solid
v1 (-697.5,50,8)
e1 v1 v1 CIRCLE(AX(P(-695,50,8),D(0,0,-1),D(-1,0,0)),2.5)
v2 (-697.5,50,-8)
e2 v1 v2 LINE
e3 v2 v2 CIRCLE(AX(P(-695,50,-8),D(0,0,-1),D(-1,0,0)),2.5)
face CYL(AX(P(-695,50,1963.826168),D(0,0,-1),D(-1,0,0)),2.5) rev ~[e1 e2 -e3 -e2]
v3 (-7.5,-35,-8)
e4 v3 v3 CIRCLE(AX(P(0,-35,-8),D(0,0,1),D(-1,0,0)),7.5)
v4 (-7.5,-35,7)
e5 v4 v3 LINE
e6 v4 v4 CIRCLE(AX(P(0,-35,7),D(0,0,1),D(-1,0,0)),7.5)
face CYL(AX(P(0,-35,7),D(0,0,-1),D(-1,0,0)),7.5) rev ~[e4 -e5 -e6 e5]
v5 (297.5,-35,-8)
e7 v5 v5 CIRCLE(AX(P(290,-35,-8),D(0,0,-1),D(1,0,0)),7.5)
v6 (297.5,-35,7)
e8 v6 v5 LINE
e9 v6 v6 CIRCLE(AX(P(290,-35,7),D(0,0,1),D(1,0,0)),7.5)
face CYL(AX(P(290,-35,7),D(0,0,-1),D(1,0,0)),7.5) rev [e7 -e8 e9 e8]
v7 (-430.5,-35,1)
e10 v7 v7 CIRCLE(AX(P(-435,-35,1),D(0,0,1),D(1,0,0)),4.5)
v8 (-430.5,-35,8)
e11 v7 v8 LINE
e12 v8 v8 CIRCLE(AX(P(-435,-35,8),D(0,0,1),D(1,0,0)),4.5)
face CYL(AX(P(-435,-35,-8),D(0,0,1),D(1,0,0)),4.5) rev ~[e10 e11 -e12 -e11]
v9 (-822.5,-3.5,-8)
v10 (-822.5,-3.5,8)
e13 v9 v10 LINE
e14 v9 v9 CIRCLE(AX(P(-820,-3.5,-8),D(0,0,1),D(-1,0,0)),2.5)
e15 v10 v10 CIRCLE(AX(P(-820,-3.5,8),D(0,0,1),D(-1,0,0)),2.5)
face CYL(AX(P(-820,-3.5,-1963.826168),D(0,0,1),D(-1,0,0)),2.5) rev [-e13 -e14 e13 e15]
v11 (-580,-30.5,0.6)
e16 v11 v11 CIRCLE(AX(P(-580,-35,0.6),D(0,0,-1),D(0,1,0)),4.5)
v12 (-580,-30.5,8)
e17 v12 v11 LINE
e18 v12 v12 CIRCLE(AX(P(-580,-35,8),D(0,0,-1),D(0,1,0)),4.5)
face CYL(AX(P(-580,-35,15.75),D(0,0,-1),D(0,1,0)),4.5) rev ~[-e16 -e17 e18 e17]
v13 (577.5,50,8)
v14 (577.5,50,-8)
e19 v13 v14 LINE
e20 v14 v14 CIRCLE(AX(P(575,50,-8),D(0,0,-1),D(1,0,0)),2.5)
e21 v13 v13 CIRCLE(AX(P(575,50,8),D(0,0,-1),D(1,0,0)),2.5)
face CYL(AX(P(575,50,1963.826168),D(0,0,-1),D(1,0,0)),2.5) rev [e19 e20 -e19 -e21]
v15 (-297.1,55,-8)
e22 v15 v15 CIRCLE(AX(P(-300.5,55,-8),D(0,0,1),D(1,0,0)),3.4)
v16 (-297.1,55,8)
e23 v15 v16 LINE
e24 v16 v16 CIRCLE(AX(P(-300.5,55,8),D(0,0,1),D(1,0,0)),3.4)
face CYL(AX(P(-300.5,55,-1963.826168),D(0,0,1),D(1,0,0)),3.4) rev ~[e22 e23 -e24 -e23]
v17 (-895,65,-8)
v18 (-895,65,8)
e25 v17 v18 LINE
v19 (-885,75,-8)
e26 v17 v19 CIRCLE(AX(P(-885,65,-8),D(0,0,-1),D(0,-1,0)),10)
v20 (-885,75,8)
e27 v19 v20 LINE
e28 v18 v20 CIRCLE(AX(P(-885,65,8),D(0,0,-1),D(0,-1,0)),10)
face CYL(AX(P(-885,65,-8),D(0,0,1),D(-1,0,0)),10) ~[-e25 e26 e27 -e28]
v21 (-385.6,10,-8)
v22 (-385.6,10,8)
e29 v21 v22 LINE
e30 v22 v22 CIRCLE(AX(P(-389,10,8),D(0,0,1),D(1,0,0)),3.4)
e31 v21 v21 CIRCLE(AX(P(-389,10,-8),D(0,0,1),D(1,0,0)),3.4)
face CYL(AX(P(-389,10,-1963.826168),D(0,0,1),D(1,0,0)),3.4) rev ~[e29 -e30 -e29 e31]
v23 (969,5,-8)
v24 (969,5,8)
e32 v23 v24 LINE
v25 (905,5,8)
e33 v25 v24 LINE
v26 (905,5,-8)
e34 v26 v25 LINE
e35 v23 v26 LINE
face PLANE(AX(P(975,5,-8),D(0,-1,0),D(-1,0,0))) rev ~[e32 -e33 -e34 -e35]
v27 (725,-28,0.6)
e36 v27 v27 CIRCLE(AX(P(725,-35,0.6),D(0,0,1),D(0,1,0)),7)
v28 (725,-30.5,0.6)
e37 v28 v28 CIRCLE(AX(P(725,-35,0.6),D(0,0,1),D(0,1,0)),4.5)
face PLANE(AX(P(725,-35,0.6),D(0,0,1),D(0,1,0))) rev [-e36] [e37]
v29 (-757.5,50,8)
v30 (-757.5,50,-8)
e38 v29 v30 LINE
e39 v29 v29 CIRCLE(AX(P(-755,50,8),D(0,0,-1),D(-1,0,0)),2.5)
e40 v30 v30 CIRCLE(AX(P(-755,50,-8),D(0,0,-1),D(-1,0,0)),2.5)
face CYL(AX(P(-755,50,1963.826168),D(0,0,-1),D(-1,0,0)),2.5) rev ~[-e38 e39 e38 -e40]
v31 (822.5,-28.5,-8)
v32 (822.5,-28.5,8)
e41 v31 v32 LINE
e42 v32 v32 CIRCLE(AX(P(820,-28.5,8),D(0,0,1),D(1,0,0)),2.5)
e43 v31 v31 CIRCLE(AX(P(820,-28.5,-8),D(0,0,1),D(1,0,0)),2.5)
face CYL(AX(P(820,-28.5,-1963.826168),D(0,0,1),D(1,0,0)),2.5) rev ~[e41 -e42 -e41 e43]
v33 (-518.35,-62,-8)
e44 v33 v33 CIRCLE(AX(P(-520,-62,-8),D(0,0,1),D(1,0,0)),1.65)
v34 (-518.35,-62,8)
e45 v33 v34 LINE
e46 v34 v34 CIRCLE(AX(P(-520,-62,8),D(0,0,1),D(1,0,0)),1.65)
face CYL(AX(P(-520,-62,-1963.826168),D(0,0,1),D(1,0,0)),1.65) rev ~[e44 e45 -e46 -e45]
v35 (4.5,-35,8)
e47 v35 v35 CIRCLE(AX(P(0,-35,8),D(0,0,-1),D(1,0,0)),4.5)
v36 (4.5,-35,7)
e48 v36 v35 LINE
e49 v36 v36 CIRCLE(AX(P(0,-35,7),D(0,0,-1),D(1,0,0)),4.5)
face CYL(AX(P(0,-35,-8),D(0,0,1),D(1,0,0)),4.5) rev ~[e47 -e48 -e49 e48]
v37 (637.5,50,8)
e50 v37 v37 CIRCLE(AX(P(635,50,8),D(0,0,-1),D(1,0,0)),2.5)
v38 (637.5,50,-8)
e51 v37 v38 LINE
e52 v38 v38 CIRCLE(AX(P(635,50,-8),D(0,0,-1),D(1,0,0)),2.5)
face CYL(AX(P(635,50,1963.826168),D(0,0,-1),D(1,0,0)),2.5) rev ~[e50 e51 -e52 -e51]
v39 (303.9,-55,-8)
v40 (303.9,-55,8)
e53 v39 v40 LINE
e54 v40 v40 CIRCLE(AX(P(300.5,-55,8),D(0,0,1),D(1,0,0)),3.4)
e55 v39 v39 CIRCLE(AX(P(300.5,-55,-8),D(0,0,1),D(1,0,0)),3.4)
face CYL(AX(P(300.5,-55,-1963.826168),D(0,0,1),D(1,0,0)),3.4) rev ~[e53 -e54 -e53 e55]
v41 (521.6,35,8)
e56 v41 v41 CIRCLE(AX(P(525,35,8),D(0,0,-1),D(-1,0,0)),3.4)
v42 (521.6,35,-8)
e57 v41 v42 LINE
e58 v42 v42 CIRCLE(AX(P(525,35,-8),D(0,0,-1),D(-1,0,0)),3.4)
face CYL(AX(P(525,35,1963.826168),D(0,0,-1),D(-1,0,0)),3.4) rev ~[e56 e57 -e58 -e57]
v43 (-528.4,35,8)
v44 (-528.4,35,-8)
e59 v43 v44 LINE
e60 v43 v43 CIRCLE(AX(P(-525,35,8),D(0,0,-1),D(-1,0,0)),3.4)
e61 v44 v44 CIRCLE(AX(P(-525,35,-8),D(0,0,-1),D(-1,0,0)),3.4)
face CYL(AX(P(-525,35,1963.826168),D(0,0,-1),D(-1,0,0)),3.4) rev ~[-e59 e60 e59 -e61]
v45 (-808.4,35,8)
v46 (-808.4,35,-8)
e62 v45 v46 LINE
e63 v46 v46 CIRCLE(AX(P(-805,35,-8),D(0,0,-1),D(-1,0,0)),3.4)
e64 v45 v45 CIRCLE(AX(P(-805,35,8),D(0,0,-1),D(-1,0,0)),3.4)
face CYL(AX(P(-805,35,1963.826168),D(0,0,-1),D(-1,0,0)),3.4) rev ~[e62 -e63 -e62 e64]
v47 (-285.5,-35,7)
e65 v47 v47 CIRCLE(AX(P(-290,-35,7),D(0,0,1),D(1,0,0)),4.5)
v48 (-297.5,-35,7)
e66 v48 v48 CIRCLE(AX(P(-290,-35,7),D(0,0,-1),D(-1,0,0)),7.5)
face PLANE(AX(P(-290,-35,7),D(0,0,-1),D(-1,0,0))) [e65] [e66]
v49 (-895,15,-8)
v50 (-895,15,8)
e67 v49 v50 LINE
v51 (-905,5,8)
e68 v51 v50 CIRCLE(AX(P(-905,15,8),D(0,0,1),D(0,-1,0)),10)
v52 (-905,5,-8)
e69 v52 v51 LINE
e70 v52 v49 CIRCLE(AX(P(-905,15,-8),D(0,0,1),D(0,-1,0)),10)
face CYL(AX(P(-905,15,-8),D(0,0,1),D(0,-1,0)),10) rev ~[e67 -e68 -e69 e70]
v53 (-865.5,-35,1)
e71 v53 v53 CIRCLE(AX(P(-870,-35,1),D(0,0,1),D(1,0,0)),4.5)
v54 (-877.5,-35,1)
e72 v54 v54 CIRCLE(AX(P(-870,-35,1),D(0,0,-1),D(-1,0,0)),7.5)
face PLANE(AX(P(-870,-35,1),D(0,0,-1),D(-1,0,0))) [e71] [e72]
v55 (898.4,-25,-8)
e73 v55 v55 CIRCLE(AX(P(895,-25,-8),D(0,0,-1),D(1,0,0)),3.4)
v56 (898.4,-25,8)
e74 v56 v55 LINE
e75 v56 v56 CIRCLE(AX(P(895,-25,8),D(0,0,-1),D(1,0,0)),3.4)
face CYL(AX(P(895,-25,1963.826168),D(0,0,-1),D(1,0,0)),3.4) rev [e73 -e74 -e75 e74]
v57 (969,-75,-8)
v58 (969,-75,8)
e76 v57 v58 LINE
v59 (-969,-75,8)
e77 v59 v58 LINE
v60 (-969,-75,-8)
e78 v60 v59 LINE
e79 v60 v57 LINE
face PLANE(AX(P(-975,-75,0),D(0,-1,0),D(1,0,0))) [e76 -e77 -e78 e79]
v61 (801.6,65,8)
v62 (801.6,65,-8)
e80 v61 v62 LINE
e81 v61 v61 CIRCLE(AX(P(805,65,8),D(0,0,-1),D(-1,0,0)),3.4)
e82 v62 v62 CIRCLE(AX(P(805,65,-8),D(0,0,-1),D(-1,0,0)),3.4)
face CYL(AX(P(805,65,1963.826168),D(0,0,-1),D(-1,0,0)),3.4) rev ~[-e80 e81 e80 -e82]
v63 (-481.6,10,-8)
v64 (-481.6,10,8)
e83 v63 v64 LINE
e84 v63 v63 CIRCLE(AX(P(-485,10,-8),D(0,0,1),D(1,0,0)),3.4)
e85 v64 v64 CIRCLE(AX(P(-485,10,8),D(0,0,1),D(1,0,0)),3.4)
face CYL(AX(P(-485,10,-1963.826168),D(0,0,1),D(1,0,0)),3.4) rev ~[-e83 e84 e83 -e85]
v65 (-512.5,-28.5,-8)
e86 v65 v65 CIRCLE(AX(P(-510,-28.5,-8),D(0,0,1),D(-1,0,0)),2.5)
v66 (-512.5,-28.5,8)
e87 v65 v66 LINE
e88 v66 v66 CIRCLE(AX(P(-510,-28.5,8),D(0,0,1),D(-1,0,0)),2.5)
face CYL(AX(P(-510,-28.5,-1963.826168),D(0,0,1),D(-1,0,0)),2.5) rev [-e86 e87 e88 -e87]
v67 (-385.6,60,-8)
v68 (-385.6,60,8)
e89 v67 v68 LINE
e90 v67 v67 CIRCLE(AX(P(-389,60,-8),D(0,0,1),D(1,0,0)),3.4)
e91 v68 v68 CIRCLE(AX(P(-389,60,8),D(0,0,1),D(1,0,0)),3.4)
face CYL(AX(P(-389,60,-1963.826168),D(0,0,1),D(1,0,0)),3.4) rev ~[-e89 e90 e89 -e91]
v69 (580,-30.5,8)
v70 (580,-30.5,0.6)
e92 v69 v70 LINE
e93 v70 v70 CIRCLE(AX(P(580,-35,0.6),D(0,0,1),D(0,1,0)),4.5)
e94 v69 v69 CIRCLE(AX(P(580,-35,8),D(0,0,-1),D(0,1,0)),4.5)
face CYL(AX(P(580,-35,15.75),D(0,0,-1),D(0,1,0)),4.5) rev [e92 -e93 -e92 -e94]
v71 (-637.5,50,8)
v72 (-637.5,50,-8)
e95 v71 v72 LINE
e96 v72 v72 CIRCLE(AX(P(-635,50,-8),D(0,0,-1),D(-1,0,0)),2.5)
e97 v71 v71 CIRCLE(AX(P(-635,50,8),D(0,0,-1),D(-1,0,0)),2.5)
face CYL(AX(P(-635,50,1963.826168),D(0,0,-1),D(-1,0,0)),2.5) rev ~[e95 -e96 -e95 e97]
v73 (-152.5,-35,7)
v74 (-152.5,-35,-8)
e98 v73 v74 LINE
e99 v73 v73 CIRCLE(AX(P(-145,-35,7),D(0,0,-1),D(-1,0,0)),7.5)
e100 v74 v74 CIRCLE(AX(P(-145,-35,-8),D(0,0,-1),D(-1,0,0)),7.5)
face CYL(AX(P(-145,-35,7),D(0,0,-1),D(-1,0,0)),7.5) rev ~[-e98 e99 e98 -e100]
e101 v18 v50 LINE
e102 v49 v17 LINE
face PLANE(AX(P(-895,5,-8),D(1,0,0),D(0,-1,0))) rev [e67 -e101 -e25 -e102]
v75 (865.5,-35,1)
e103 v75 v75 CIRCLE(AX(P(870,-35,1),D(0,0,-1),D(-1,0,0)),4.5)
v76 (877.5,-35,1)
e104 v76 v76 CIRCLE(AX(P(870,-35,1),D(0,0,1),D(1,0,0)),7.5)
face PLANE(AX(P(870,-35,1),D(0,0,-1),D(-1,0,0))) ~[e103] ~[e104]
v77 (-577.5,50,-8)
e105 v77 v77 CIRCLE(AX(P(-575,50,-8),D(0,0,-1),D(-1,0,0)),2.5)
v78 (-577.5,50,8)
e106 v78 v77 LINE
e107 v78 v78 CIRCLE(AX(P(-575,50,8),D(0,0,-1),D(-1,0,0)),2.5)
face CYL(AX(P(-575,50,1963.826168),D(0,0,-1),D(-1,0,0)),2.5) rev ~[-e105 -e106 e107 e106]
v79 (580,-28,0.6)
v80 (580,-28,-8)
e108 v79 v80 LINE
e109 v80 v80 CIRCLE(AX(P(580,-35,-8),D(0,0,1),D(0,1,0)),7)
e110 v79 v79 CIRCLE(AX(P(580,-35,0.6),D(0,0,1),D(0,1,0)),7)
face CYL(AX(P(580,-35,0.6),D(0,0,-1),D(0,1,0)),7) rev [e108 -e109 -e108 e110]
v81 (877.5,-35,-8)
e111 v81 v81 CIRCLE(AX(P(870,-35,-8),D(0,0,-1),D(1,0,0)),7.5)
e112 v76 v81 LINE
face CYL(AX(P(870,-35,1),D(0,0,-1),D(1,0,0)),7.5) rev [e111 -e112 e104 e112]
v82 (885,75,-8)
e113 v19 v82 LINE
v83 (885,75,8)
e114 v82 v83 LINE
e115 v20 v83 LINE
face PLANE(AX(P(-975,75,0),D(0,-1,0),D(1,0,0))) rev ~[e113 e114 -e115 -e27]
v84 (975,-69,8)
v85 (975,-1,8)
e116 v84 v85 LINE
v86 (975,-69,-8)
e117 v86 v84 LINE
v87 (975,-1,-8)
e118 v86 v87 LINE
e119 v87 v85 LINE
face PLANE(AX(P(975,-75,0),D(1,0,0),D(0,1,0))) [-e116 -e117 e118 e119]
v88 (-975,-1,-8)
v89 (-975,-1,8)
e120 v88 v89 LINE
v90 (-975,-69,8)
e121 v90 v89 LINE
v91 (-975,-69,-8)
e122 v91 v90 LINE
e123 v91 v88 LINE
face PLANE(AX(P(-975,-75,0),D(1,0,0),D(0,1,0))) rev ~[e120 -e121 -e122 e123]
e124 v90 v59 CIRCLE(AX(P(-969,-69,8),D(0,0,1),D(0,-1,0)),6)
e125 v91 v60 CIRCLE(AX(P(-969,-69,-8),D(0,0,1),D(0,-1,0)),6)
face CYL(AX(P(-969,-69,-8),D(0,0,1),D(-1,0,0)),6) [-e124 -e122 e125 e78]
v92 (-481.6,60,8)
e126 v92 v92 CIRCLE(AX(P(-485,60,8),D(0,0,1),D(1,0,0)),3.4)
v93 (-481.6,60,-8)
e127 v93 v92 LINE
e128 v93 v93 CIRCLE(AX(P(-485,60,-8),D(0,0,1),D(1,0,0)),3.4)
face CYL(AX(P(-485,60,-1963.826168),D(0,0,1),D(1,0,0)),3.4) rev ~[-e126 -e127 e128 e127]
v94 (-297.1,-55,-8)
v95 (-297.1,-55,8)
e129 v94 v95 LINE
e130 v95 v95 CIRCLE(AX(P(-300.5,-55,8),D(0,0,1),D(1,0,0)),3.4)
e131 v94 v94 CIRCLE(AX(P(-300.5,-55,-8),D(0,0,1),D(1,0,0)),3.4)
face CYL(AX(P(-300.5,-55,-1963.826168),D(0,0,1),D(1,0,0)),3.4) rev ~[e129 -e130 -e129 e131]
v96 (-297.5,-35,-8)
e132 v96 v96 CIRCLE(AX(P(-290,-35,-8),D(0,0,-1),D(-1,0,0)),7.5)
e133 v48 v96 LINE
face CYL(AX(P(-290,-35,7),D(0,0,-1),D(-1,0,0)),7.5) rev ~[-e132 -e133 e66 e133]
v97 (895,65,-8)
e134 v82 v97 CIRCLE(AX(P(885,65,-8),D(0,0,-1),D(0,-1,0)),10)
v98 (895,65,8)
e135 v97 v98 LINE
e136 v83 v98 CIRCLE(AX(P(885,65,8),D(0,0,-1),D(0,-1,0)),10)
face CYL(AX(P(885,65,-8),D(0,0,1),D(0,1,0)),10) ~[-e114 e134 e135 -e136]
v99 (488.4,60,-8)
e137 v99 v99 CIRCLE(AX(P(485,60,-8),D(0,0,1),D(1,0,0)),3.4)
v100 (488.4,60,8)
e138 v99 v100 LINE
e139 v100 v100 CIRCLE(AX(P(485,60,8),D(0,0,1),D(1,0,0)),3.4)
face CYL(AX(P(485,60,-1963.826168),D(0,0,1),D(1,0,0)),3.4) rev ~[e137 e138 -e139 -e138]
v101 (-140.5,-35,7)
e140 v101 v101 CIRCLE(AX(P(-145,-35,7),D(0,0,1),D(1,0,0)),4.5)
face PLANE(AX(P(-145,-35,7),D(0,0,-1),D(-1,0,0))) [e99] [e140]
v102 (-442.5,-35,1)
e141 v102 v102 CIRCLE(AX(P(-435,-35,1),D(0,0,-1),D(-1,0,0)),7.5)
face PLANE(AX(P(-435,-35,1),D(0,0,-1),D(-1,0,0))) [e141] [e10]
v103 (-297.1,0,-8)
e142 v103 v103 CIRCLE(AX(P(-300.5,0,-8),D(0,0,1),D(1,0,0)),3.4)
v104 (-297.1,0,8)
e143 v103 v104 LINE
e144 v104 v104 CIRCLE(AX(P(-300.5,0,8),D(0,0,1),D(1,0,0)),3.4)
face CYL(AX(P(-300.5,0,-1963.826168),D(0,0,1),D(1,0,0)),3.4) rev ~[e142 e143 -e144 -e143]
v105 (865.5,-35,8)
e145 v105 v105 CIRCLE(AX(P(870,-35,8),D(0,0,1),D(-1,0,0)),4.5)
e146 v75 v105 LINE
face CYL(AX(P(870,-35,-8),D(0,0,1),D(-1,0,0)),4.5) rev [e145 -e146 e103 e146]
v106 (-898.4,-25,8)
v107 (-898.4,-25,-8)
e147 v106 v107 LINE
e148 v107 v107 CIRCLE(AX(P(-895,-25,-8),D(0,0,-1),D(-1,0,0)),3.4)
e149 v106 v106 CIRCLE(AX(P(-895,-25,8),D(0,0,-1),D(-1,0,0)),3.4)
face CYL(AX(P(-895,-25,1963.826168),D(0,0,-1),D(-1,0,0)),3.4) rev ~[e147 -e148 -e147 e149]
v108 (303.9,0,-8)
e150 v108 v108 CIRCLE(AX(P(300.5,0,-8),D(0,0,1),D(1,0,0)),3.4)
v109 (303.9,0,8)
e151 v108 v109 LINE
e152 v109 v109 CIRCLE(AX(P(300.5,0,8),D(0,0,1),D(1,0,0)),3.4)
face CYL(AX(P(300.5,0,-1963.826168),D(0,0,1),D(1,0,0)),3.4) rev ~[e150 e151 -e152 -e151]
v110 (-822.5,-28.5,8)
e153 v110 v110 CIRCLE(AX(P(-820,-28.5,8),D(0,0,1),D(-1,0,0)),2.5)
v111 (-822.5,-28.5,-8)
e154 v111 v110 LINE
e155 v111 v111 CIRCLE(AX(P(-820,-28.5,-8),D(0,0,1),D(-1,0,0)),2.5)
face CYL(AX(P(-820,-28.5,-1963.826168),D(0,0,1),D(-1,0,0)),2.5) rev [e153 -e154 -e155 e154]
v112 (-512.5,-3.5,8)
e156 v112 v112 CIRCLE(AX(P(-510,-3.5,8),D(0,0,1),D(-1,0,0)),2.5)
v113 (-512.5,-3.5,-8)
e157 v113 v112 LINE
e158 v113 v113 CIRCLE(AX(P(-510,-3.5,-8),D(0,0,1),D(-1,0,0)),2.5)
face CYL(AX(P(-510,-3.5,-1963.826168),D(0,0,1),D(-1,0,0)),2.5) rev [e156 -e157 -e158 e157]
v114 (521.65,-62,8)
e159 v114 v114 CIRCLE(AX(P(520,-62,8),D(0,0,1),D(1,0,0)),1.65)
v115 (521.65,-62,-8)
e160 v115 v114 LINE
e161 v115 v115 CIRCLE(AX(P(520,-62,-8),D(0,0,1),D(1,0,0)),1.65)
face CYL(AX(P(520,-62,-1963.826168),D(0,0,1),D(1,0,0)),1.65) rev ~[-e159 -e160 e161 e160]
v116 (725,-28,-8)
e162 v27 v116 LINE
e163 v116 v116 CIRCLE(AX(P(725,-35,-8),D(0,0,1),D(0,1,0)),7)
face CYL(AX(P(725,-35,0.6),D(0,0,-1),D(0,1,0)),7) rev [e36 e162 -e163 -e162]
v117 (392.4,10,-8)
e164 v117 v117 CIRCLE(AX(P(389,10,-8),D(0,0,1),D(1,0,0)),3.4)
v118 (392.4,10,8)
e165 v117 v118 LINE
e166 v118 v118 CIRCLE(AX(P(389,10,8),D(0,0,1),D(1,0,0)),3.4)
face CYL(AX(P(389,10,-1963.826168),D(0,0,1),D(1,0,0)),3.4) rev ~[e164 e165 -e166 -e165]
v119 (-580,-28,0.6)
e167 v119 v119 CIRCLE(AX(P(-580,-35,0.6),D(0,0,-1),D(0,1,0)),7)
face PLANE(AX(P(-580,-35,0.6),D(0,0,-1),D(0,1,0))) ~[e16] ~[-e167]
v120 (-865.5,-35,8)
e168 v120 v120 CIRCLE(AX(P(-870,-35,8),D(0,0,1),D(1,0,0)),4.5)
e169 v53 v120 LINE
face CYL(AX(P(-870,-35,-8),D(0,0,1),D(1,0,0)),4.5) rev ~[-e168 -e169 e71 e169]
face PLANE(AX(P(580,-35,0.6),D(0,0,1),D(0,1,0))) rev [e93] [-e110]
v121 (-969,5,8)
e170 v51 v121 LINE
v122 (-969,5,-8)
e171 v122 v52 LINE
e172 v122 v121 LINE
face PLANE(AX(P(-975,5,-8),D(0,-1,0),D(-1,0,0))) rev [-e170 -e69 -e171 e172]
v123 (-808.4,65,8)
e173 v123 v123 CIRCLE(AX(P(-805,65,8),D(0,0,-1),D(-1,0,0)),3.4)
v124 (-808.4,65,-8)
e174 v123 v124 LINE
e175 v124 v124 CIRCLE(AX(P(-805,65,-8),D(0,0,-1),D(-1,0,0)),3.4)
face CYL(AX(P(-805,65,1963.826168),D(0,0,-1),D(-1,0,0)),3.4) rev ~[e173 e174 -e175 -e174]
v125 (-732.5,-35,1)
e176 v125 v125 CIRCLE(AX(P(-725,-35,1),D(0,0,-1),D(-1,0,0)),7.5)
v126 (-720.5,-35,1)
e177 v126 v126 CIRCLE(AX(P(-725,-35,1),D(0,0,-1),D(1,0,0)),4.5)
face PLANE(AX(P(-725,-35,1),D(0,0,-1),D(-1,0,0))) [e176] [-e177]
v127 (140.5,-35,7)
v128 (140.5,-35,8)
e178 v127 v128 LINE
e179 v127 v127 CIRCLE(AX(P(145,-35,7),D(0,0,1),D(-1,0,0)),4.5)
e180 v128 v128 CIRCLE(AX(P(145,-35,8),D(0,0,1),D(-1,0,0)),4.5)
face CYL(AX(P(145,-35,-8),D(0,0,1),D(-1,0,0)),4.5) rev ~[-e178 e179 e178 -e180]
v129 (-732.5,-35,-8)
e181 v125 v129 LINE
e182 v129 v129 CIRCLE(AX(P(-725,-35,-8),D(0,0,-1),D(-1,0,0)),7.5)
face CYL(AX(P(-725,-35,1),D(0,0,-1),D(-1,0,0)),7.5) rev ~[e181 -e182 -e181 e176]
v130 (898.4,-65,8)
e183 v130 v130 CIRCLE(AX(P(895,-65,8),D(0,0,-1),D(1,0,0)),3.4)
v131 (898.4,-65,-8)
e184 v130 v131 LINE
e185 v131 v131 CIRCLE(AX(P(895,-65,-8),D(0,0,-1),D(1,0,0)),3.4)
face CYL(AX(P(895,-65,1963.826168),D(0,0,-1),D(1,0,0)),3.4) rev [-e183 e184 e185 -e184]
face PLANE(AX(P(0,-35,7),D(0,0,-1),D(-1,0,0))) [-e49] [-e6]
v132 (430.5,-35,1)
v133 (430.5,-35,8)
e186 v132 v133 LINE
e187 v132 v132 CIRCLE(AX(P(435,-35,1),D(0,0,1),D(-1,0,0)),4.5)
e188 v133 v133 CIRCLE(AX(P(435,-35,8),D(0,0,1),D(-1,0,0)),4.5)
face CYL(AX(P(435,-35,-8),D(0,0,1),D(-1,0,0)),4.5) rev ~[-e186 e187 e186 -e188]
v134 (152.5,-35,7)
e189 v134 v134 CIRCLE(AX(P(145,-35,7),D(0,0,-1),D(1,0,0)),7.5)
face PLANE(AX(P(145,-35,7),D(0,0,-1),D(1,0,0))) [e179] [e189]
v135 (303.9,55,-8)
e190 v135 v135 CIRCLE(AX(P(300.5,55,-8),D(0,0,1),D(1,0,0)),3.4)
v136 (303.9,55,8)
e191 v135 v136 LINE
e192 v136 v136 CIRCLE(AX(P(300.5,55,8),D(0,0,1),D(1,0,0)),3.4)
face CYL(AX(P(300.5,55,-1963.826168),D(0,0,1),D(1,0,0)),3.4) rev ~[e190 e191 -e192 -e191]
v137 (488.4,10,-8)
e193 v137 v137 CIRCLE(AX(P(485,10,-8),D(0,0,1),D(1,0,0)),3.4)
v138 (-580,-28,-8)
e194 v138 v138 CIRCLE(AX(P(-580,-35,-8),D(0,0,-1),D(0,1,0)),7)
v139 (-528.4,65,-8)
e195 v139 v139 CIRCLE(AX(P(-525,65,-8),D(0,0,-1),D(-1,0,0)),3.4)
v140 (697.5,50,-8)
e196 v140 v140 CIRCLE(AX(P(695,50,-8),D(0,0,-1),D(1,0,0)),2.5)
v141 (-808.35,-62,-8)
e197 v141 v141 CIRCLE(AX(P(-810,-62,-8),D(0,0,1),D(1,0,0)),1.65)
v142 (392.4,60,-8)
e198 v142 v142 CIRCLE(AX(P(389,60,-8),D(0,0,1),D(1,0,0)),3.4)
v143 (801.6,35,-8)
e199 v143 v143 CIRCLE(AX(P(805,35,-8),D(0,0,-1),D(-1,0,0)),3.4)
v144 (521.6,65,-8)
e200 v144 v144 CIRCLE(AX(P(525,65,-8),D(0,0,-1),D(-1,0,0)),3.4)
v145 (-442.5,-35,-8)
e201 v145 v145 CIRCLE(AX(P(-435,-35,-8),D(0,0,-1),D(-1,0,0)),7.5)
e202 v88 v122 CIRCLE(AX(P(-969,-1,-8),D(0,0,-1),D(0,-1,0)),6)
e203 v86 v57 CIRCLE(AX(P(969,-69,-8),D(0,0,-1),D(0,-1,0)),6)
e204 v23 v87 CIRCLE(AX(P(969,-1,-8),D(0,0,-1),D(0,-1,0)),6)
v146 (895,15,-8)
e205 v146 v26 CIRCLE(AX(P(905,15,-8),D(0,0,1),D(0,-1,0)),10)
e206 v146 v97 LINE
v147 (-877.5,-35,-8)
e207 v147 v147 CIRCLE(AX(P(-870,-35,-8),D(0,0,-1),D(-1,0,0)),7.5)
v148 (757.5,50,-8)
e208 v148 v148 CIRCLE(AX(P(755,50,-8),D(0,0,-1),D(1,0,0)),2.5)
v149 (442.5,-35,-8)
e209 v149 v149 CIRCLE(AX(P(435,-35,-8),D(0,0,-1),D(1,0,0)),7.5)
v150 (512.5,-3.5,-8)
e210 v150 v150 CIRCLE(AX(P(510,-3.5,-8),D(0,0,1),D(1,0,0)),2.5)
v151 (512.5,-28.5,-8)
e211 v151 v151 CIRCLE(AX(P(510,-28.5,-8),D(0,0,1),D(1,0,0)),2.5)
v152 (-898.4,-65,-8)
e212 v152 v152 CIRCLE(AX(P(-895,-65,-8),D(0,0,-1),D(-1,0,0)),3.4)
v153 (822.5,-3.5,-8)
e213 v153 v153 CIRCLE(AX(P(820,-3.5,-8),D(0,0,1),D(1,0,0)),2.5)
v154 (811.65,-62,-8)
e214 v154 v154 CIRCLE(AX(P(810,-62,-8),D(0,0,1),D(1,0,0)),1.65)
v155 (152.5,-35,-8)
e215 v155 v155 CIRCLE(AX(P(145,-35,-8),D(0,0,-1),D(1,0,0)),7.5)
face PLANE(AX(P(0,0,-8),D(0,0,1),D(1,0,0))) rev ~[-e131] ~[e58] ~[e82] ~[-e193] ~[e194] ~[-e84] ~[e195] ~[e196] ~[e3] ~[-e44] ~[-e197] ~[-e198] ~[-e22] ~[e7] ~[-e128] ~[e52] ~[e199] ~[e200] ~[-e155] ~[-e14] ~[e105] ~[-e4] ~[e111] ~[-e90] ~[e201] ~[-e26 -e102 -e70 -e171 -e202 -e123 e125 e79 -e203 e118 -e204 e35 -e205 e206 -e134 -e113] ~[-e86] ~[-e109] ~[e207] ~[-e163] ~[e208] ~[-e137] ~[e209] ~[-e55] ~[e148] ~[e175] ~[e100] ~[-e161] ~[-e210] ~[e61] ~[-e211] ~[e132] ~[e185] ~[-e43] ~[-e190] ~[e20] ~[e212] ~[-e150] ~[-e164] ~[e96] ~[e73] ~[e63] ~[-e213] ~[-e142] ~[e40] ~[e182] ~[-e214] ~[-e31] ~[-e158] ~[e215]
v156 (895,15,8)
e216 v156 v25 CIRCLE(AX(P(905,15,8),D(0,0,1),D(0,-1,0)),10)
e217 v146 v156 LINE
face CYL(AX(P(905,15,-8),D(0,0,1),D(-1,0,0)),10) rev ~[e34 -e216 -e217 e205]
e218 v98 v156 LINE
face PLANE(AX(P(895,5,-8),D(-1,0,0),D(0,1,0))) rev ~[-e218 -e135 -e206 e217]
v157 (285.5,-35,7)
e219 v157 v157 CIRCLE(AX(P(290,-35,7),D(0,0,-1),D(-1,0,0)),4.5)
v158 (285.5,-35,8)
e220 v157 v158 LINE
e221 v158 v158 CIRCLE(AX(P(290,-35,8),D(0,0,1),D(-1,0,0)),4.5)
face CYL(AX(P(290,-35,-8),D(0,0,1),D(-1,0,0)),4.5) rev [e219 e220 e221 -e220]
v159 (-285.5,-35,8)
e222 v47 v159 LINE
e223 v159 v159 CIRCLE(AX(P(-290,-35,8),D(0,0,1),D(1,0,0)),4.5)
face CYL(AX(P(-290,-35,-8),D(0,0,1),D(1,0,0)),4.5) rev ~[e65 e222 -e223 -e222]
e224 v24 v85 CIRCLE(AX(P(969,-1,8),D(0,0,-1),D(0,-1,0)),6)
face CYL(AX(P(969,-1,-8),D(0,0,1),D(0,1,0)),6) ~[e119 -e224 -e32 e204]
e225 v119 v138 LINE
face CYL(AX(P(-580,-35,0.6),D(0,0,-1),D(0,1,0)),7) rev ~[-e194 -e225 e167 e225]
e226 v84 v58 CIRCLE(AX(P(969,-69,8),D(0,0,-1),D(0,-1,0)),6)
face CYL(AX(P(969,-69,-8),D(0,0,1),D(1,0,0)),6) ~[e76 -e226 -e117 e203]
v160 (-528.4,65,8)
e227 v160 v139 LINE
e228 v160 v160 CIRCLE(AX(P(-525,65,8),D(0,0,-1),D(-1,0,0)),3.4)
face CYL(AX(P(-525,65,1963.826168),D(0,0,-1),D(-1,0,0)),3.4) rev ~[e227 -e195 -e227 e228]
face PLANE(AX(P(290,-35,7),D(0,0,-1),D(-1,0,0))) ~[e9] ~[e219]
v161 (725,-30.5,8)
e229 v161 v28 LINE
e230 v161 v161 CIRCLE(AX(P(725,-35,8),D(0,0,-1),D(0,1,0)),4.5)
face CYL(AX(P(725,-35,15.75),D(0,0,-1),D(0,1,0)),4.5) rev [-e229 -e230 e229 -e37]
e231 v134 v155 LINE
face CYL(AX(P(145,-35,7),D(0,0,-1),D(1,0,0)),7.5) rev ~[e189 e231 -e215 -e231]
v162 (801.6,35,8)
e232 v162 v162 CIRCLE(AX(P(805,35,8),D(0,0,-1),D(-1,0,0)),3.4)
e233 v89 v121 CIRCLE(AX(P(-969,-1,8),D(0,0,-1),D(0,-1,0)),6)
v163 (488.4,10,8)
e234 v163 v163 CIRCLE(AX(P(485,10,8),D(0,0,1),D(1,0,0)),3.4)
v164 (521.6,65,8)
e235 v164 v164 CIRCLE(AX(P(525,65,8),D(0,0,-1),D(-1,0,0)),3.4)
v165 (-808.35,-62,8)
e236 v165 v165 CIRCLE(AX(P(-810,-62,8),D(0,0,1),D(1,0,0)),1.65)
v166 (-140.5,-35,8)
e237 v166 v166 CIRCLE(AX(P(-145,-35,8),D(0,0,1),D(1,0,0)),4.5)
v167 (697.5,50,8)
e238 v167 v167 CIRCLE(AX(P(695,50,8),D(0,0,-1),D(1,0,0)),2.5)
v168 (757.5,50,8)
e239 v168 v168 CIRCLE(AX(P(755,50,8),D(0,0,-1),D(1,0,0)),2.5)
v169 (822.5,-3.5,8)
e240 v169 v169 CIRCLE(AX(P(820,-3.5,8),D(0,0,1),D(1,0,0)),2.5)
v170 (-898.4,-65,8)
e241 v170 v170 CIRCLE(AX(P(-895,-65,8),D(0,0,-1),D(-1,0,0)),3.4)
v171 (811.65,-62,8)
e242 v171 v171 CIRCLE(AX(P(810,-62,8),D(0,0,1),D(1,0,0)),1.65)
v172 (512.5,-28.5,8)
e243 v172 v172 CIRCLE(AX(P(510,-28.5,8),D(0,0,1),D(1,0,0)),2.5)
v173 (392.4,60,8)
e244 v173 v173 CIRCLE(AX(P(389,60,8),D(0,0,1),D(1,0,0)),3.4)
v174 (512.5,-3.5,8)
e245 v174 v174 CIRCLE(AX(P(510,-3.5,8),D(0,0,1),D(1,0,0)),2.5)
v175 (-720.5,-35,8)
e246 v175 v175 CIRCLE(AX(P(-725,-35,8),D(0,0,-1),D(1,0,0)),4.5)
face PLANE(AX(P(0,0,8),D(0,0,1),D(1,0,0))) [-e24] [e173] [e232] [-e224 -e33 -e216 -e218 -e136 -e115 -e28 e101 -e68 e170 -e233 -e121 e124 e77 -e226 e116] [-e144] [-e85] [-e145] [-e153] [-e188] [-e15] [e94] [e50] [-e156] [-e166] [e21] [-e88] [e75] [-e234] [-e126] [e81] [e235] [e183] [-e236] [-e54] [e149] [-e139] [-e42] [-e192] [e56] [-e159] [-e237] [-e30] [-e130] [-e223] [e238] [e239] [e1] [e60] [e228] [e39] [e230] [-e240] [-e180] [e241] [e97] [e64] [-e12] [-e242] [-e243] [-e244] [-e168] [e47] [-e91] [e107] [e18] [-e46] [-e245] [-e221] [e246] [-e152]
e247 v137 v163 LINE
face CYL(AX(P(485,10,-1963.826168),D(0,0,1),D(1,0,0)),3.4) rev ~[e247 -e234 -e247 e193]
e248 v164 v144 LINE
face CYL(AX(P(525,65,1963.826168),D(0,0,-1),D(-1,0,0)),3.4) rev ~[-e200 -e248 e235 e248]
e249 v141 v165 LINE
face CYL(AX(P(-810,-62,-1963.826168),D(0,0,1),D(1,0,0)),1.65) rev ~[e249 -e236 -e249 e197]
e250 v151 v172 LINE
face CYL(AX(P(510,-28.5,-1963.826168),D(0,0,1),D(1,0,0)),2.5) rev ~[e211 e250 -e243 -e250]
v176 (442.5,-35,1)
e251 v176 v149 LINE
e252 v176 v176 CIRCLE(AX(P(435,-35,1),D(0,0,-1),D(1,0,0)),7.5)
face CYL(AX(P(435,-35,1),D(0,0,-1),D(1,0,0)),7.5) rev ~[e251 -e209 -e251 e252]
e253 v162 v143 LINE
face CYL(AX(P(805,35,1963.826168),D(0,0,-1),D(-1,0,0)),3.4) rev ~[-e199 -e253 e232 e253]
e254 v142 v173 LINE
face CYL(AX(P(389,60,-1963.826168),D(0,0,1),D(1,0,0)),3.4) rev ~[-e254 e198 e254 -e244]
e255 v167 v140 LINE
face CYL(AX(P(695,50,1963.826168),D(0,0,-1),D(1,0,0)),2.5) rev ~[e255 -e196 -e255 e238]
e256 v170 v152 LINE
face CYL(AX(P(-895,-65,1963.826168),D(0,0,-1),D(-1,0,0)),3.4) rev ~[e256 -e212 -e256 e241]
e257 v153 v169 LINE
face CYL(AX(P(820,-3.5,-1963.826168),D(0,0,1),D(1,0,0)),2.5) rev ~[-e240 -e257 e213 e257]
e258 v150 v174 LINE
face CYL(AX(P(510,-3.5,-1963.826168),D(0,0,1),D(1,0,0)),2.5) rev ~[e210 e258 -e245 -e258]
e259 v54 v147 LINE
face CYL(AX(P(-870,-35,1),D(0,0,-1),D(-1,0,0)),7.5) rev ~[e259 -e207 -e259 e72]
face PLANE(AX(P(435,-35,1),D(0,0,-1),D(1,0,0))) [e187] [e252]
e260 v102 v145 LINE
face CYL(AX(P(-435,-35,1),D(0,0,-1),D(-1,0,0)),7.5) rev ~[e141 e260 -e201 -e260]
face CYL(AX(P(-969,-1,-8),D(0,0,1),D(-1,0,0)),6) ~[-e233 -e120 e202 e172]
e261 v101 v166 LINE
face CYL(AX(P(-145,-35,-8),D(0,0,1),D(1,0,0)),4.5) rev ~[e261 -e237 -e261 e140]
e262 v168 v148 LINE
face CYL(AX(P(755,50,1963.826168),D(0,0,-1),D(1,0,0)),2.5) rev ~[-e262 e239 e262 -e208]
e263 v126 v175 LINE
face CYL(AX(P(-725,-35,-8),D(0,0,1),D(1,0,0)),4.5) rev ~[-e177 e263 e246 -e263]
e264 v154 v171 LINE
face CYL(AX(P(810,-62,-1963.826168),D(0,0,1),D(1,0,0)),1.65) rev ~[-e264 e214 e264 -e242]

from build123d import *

# Parameters (mm, degrees)
SKETCH_6_W                     = 1950
SKETCH_6_H                     = 150
EXTRUDE_2_DEPTH                = 8
HOLE_WIZARD_M8_1_D             = 6.8
HOLE_WIZARD_M6_2_D             = 5
PATTERN_LINEAR_1_COUNT         = 4
PATTERN_LINEAR_1_PITCH         = 60
MIRROR_1_COPY_1_D              = 5
MIRROR_1_COPY_2_D              = 5
MIRROR_1_COPY_3_D              = 5
HOLE_WIZARD_M8_1_2_D           = 9
HOLE_WIZARD_M8_1_2_CBORE_D     = 15
HOLE_WIZARD_M8_1_2_CBORE_DEPTH = 9
PATTERN_LINEAR_3_COUNT         = 2
PATTERN_LINEAR_3_PITCH         = 145
PATTERN_LINEAR_4_COUNT         = 2
PATTERN_LINEAR_4_PITCH         = 435
HOLE_WIZARD_M8_2_D             = 9
HOLE_WIZARD_M8_2_CBORE_D       = 15
HOLE_WIZARD_M8_2_CBORE_DEPTH   = 15
PATTERN_LINEAR_5_COUNT         = 3
PATTERN_LINEAR_5_PITCH         = 145
MIRROR_4_COPY_1_D              = 9
MIRROR_4_COPY_1_CBORE_D        = 15
MIRROR_4_COPY_1_CBORE_DEPTH    = 9
MIRROR_4_COPY_2_D              = 9
MIRROR_4_COPY_2_CBORE_D        = 15
MIRROR_4_COPY_2_CBORE_DEPTH    = 15
MIRROR_4_COPY_3_D              = 9
MIRROR_4_COPY_3_CBORE_D        = 15
MIRROR_4_COPY_3_CBORE_DEPTH    = 15
SKETCH_29_W                    = 80
SKETCH_29_H                    = 70
CUT_EXTRUDE_1_DEPTH            = 979.011247379
HOLE_WIZARD_M8_6_D             = 6.8
PATTERN_LINEAR_6_COUNT         = 2
PATTERN_LINEAR_6_PITCH         = 145
FILLET_1_R                     = 6
HOLE_WIZARD_M6_1_D             = 5
FILLET_2_R                     = 10
FILLET_3_R                     = 10
HOLE_WIZARD_M8_7_D             = 6.8
HOLE_WIZARD_M8_8_D             = 6.8
HOLE_WIZARD_M4_1_D             = 3.3
HOLE_WIZARD_M4_2_D             = 3.3


with BuildPart() as part:
    # 草图6 → 凸台-拉伸2 (new, symmetric)
    with BuildSketch(Plane.XY):
        Rectangle(SKETCH_6_W, SKETCH_6_H)
    extrude(amount=EXTRUDE_2_DEPTH, both=True)

    # Hole Wizard M8 _1 (through all)
    with Locations(Plane.XY.offset(8)):
        with Locations((-805, 65), (-805, 35), (-525, 65), (-525, 35), (805, 35), (805, 65), (525, 35), (525, 65)):
            Hole(HOLE_WIZARD_M8_1_D / 2)

    # M6 螺纹孔2 (through all)
    with Locations(Plane.XY.offset(8)):
        with Locations((-575, 50)):
            hole_wizard_m6_2 = Hole(HOLE_WIZARD_M6_2_D / 2)

    # 阵列(线性)1: M6 螺纹孔2 ×4
    with Locations(*[(-i * PATTERN_LINEAR_1_PITCH, 0, 0) for i in range(1, PATTERN_LINEAR_1_COUNT)]):
        add(hole_wizard_m6_2, mode=Mode.SUBTRACT)

    # 镜向1: M6 螺纹孔2 across plane
    add(hole_wizard_m6_2.mirror(Plane(origin=(0, 0, 0), x_dir=(0, 0, 1), z_dir=(1, 0, 0))), mode=Mode.SUBTRACT)

    # 镜向1 copy 1 (through all)
    with Locations(Plane(origin=(60, 0, 8), x_dir=(-1, 0, 0), z_dir=(0, 0, 1))):
        with Locations((-575, -50)):
            Hole(MIRROR_1_COPY_1_D / 2)

    # 镜向1 copy 2 (through all)
    with Locations(Plane(origin=(120, 0, 8), x_dir=(-1, 0, 0), z_dir=(0, 0, 1))):
        with Locations((-575, -50)):
            Hole(MIRROR_1_COPY_2_D / 2)

    # 镜向1 copy 3 (through all)
    with Locations(Plane(origin=(180, 0, 8), x_dir=(-1, 0, 0), z_dir=(0, 0, 1))):
        with Locations((-575, -50)):
            Hole(MIRROR_1_COPY_3_D / 2)

    # Hole Wizard M8 _1 2 (through all)
    with Locations(Plane(origin=(0, 0, -8), x_dir=(-1, 0, 0), z_dir=(0, 0, -1))):
        with Locations((870, -35)):
            hole_wizard_m8_1_2 = CounterBoreHole(HOLE_WIZARD_M8_1_2_D / 2, HOLE_WIZARD_M8_1_2_CBORE_D / 2, HOLE_WIZARD_M8_1_2_CBORE_DEPTH)

    # 阵列(线性)3: Hole Wizard M8 _1 2 ×2
    with Locations(*[(i * PATTERN_LINEAR_3_PITCH, 0, 0) for i in range(1, PATTERN_LINEAR_3_COUNT)]):
        add(hole_wizard_m8_1_2, mode=Mode.SUBTRACT)

    # 阵列(线性)4: Hole Wizard M8 _1 2 ×2
    with Locations(*[(i * PATTERN_LINEAR_4_PITCH, 0, 0) for i in range(1, PATTERN_LINEAR_4_COUNT)]):
        add(hole_wizard_m8_1_2, mode=Mode.SUBTRACT)

    # M8 六角凹头螺钉的柱形沉头孔2 (through all)
    with Locations(Plane(origin=(0, 0, -8), x_dir=(-1, 0, 0), z_dir=(0, 0, -1))):
        with Locations((290, -35)):
            hole_wizard_m8_2 = CounterBoreHole(HOLE_WIZARD_M8_2_D / 2, HOLE_WIZARD_M8_2_CBORE_D / 2, HOLE_WIZARD_M8_2_CBORE_DEPTH)

    # 阵列(线性)5: M8 六角凹头螺钉的柱形沉头孔2 ×3
    with Locations(*[(i * PATTERN_LINEAR_5_PITCH, 0, 0) for i in range(1, PATTERN_LINEAR_5_COUNT)]):
        add(hole_wizard_m8_2, mode=Mode.SUBTRACT)

    # 镜向4: Hole Wizard M8 _1 2, M8 六角凹头螺钉的柱形沉头孔2 across plane
    add(hole_wizard_m8_1_2.mirror(Plane(origin=(0, 0, 0), x_dir=(0, 0, 1), z_dir=(1, 0, 0))), mode=Mode.SUBTRACT)
    add(hole_wizard_m8_2.mirror(Plane(origin=(0, 0, 0), x_dir=(0, 0, 1), z_dir=(1, 0, 0))), mode=Mode.SUBTRACT)

    # 镜向4 copy 1 (through all)
    with Locations(Plane(origin=(-435, 0, -8), x_dir=(1, 0, 0), z_dir=(0, 0, -1))):
        with Locations((870, 35)):
            CounterBoreHole(MIRROR_4_COPY_1_D / 2, MIRROR_4_COPY_1_CBORE_D / 2, MIRROR_4_COPY_1_CBORE_DEPTH)

    # 镜向4 copy 2 (through all)
    with Locations(Plane(origin=(-145, 0, -8), x_dir=(1, 0, 0), z_dir=(0, 0, -1))):
        with Locations((290, 35)):
            CounterBoreHole(MIRROR_4_COPY_2_D / 2, MIRROR_4_COPY_2_CBORE_D / 2, MIRROR_4_COPY_2_CBORE_DEPTH)

    # 镜向4 copy 3 (through all)
    with Locations(Plane(origin=(-290, 0, -8), x_dir=(1, 0, 0), z_dir=(0, 0, -1))):
        with Locations((290, 35)):
            CounterBoreHole(MIRROR_4_COPY_3_D / 2, MIRROR_4_COPY_3_CBORE_D / 2, MIRROR_4_COPY_3_CBORE_DEPTH)

    # 草图27 → M8 六角凹头螺钉的柱形沉头孔3 (revolve, cut)
    with BuildSketch(Plane(origin=(725, -35, -8), x_dir=(0, 1, 0), z_dir=(1, 0, 0))):
        Polygon((0, 0), (0, 26.453872786), (4.5, 23.75), (4.5, 8.6), (7, 8.6), (7, 0), align=None)
    hole_wizard_m8_3 = revolve(axis=Axis((725, -35, -14.35), (0, 0, 1)), mode=Mode.SUBTRACT)

    # 草图29 → 切除-拉伸1 (cut, through all)
    with BuildSketch(Plane(origin=(0, 0, -8), x_dir=(-1, 0, 0), z_dir=(0, 0, -1))):
        with Locations((-935, 40)):
            Rectangle(SKETCH_29_W, SKETCH_29_H)
    cut_extrude_1 = extrude(amount=-CUT_EXTRUDE_1_DEPTH, mode=Mode.SUBTRACT)

    # 镜向5: 切除-拉伸1 across plane
    add(cut_extrude_1.mirror(Plane(origin=(0, 0, 0), x_dir=(0, 0, 1), z_dir=(1, 0, 0))), mode=Mode.SUBTRACT)

    # M8 螺纹孔6 (through all)
    with Locations(Plane.XY.offset(8)):
        with Locations((-895, -65), (-895, -25)):
            hole_wizard_m8_6 = Hole(HOLE_WIZARD_M8_6_D / 2)

    # 镜向7: M8 螺纹孔6 across plane
    add(hole_wizard_m8_6.mirror(Plane(origin=(0, 0, 0), x_dir=(0, 0, 1), z_dir=(1, 0, 0))), mode=Mode.SUBTRACT)

    # 阵列(线性)6: M8 六角凹头螺钉的柱形沉头孔3 ×2
    with Locations(*[(-i * PATTERN_LINEAR_6_PITCH, 0, 0) for i in range(1, PATTERN_LINEAR_6_COUNT)]):
        add(hole_wizard_m8_3, mode=Mode.SUBTRACT)

    # 镜向8 copy 1 sketch → 镜向8 copy 1 (revolve, cut)
    with BuildSketch(Plane(origin=(-580, -35, -8), x_dir=(0, 1, 0), z_dir=(-1, 0, 0))):
        Polygon((0, 0), (0, -26.453872786), (4.5, -23.75), (4.5, -8.6), (7, -8.6), (7, 0), align=None)
    revolve(axis=Axis((-580, -35, -14.35), (0, 0, -1)), mode=Mode.SUBTRACT)

    # 镜向8 copy 2 sketch → 镜向8 copy 2 (revolve, cut)
    with BuildSketch(Plane(origin=(-725, -35, -8), x_dir=(0, 1, 0), z_dir=(-1, 0, 0))):
        Polygon((0, 0), (0, -26.453872786), (4.5, -23.75), (4.5, -8.6), (7, -8.6), (7, 0), align=None)
    revolve(axis=Axis((-725, -35, -14.35), (0, 0, -1)), mode=Mode.SUBTRACT)

    # 圆角1
    fillet_1_edges = [part.edges().sort_by_distance(p)[0] for p in [
        (975, 5, 0),
        (-975, 5, 0),
        (975, -75, 0),
        (-975, -75, 0),
    ]]
    fillet(fillet_1_edges, radius=FILLET_1_R)

    # M6 螺纹孔1 (through all)
    with Locations(Plane(origin=(0, 0, -8), x_dir=(-1, 0, 0), z_dir=(0, 0, -1))):
        with Locations((-820, -3.5), (-820, -28.5), (-510, -3.5), (-510, -28.5)):
            hole_wizard_m6_1 = Hole(HOLE_WIZARD_M6_1_D / 2)

    # 镜向9: M6 螺纹孔1 across plane
    add(hole_wizard_m6_1.mirror(Plane(origin=(0, 0, 0), x_dir=(0, 0, 1), z_dir=(1, 0, 0))), mode=Mode.SUBTRACT)

    # 圆角2
    fillet_2_edges = [part.edges().sort_by_distance(p)[0] for p in [
        (895, 5, 0),
        (-895, 5, 0),
    ]]
    fillet(fillet_2_edges, radius=FILLET_2_R)

    # 圆角3
    fillet_3_edges = [part.edges().sort_by_distance(p)[0] for p in [
        (895, 75, 0),
        (-895, 75, 0),
    ]]
    fillet(fillet_3_edges, radius=FILLET_3_R)

    # M8 螺纹孔7 (through all)
    with Locations(Plane(origin=(0, 0, -8), x_dir=(-1, 0, 0), z_dir=(0, 0, -1))):
        with Locations((-300.5, 55), (-300.5, 0), (-300.5, -55), (300.5, -55), (300.5, 0), (300.5, 55)):
            Hole(HOLE_WIZARD_M8_7_D / 2)

    # M8 螺纹孔8 (through all)
    with Locations(Plane(origin=(0, 0, -8), x_dir=(-1, 0, 0), z_dir=(0, 0, -1))):
        with Locations((-389, 60), (-389, 10), (-485, 10), (-485, 60), (485, 60), (485, 10), (389, 10), (389, 60)):
            Hole(HOLE_WIZARD_M8_8_D / 2)

    # M4 螺纹孔1 (through all)
    with Locations(Plane(origin=(0, 0, -8), x_dir=(-1, 0, 0), z_dir=(0, 0, -1))):
        with Locations((520, -62), (810, -62)):
            Hole(HOLE_WIZARD_M4_1_D / 2)

    # M4 螺纹孔2 (through all)
    with Locations(Plane(origin=(0, 0, -8), x_dir=(-1, 0, 0), z_dir=(0, 0, -1))):
        with Locations((-520, -62), (-810, -62)):
            Hole(HOLE_WIZARD_M4_2_D / 2)


solid = part.part
